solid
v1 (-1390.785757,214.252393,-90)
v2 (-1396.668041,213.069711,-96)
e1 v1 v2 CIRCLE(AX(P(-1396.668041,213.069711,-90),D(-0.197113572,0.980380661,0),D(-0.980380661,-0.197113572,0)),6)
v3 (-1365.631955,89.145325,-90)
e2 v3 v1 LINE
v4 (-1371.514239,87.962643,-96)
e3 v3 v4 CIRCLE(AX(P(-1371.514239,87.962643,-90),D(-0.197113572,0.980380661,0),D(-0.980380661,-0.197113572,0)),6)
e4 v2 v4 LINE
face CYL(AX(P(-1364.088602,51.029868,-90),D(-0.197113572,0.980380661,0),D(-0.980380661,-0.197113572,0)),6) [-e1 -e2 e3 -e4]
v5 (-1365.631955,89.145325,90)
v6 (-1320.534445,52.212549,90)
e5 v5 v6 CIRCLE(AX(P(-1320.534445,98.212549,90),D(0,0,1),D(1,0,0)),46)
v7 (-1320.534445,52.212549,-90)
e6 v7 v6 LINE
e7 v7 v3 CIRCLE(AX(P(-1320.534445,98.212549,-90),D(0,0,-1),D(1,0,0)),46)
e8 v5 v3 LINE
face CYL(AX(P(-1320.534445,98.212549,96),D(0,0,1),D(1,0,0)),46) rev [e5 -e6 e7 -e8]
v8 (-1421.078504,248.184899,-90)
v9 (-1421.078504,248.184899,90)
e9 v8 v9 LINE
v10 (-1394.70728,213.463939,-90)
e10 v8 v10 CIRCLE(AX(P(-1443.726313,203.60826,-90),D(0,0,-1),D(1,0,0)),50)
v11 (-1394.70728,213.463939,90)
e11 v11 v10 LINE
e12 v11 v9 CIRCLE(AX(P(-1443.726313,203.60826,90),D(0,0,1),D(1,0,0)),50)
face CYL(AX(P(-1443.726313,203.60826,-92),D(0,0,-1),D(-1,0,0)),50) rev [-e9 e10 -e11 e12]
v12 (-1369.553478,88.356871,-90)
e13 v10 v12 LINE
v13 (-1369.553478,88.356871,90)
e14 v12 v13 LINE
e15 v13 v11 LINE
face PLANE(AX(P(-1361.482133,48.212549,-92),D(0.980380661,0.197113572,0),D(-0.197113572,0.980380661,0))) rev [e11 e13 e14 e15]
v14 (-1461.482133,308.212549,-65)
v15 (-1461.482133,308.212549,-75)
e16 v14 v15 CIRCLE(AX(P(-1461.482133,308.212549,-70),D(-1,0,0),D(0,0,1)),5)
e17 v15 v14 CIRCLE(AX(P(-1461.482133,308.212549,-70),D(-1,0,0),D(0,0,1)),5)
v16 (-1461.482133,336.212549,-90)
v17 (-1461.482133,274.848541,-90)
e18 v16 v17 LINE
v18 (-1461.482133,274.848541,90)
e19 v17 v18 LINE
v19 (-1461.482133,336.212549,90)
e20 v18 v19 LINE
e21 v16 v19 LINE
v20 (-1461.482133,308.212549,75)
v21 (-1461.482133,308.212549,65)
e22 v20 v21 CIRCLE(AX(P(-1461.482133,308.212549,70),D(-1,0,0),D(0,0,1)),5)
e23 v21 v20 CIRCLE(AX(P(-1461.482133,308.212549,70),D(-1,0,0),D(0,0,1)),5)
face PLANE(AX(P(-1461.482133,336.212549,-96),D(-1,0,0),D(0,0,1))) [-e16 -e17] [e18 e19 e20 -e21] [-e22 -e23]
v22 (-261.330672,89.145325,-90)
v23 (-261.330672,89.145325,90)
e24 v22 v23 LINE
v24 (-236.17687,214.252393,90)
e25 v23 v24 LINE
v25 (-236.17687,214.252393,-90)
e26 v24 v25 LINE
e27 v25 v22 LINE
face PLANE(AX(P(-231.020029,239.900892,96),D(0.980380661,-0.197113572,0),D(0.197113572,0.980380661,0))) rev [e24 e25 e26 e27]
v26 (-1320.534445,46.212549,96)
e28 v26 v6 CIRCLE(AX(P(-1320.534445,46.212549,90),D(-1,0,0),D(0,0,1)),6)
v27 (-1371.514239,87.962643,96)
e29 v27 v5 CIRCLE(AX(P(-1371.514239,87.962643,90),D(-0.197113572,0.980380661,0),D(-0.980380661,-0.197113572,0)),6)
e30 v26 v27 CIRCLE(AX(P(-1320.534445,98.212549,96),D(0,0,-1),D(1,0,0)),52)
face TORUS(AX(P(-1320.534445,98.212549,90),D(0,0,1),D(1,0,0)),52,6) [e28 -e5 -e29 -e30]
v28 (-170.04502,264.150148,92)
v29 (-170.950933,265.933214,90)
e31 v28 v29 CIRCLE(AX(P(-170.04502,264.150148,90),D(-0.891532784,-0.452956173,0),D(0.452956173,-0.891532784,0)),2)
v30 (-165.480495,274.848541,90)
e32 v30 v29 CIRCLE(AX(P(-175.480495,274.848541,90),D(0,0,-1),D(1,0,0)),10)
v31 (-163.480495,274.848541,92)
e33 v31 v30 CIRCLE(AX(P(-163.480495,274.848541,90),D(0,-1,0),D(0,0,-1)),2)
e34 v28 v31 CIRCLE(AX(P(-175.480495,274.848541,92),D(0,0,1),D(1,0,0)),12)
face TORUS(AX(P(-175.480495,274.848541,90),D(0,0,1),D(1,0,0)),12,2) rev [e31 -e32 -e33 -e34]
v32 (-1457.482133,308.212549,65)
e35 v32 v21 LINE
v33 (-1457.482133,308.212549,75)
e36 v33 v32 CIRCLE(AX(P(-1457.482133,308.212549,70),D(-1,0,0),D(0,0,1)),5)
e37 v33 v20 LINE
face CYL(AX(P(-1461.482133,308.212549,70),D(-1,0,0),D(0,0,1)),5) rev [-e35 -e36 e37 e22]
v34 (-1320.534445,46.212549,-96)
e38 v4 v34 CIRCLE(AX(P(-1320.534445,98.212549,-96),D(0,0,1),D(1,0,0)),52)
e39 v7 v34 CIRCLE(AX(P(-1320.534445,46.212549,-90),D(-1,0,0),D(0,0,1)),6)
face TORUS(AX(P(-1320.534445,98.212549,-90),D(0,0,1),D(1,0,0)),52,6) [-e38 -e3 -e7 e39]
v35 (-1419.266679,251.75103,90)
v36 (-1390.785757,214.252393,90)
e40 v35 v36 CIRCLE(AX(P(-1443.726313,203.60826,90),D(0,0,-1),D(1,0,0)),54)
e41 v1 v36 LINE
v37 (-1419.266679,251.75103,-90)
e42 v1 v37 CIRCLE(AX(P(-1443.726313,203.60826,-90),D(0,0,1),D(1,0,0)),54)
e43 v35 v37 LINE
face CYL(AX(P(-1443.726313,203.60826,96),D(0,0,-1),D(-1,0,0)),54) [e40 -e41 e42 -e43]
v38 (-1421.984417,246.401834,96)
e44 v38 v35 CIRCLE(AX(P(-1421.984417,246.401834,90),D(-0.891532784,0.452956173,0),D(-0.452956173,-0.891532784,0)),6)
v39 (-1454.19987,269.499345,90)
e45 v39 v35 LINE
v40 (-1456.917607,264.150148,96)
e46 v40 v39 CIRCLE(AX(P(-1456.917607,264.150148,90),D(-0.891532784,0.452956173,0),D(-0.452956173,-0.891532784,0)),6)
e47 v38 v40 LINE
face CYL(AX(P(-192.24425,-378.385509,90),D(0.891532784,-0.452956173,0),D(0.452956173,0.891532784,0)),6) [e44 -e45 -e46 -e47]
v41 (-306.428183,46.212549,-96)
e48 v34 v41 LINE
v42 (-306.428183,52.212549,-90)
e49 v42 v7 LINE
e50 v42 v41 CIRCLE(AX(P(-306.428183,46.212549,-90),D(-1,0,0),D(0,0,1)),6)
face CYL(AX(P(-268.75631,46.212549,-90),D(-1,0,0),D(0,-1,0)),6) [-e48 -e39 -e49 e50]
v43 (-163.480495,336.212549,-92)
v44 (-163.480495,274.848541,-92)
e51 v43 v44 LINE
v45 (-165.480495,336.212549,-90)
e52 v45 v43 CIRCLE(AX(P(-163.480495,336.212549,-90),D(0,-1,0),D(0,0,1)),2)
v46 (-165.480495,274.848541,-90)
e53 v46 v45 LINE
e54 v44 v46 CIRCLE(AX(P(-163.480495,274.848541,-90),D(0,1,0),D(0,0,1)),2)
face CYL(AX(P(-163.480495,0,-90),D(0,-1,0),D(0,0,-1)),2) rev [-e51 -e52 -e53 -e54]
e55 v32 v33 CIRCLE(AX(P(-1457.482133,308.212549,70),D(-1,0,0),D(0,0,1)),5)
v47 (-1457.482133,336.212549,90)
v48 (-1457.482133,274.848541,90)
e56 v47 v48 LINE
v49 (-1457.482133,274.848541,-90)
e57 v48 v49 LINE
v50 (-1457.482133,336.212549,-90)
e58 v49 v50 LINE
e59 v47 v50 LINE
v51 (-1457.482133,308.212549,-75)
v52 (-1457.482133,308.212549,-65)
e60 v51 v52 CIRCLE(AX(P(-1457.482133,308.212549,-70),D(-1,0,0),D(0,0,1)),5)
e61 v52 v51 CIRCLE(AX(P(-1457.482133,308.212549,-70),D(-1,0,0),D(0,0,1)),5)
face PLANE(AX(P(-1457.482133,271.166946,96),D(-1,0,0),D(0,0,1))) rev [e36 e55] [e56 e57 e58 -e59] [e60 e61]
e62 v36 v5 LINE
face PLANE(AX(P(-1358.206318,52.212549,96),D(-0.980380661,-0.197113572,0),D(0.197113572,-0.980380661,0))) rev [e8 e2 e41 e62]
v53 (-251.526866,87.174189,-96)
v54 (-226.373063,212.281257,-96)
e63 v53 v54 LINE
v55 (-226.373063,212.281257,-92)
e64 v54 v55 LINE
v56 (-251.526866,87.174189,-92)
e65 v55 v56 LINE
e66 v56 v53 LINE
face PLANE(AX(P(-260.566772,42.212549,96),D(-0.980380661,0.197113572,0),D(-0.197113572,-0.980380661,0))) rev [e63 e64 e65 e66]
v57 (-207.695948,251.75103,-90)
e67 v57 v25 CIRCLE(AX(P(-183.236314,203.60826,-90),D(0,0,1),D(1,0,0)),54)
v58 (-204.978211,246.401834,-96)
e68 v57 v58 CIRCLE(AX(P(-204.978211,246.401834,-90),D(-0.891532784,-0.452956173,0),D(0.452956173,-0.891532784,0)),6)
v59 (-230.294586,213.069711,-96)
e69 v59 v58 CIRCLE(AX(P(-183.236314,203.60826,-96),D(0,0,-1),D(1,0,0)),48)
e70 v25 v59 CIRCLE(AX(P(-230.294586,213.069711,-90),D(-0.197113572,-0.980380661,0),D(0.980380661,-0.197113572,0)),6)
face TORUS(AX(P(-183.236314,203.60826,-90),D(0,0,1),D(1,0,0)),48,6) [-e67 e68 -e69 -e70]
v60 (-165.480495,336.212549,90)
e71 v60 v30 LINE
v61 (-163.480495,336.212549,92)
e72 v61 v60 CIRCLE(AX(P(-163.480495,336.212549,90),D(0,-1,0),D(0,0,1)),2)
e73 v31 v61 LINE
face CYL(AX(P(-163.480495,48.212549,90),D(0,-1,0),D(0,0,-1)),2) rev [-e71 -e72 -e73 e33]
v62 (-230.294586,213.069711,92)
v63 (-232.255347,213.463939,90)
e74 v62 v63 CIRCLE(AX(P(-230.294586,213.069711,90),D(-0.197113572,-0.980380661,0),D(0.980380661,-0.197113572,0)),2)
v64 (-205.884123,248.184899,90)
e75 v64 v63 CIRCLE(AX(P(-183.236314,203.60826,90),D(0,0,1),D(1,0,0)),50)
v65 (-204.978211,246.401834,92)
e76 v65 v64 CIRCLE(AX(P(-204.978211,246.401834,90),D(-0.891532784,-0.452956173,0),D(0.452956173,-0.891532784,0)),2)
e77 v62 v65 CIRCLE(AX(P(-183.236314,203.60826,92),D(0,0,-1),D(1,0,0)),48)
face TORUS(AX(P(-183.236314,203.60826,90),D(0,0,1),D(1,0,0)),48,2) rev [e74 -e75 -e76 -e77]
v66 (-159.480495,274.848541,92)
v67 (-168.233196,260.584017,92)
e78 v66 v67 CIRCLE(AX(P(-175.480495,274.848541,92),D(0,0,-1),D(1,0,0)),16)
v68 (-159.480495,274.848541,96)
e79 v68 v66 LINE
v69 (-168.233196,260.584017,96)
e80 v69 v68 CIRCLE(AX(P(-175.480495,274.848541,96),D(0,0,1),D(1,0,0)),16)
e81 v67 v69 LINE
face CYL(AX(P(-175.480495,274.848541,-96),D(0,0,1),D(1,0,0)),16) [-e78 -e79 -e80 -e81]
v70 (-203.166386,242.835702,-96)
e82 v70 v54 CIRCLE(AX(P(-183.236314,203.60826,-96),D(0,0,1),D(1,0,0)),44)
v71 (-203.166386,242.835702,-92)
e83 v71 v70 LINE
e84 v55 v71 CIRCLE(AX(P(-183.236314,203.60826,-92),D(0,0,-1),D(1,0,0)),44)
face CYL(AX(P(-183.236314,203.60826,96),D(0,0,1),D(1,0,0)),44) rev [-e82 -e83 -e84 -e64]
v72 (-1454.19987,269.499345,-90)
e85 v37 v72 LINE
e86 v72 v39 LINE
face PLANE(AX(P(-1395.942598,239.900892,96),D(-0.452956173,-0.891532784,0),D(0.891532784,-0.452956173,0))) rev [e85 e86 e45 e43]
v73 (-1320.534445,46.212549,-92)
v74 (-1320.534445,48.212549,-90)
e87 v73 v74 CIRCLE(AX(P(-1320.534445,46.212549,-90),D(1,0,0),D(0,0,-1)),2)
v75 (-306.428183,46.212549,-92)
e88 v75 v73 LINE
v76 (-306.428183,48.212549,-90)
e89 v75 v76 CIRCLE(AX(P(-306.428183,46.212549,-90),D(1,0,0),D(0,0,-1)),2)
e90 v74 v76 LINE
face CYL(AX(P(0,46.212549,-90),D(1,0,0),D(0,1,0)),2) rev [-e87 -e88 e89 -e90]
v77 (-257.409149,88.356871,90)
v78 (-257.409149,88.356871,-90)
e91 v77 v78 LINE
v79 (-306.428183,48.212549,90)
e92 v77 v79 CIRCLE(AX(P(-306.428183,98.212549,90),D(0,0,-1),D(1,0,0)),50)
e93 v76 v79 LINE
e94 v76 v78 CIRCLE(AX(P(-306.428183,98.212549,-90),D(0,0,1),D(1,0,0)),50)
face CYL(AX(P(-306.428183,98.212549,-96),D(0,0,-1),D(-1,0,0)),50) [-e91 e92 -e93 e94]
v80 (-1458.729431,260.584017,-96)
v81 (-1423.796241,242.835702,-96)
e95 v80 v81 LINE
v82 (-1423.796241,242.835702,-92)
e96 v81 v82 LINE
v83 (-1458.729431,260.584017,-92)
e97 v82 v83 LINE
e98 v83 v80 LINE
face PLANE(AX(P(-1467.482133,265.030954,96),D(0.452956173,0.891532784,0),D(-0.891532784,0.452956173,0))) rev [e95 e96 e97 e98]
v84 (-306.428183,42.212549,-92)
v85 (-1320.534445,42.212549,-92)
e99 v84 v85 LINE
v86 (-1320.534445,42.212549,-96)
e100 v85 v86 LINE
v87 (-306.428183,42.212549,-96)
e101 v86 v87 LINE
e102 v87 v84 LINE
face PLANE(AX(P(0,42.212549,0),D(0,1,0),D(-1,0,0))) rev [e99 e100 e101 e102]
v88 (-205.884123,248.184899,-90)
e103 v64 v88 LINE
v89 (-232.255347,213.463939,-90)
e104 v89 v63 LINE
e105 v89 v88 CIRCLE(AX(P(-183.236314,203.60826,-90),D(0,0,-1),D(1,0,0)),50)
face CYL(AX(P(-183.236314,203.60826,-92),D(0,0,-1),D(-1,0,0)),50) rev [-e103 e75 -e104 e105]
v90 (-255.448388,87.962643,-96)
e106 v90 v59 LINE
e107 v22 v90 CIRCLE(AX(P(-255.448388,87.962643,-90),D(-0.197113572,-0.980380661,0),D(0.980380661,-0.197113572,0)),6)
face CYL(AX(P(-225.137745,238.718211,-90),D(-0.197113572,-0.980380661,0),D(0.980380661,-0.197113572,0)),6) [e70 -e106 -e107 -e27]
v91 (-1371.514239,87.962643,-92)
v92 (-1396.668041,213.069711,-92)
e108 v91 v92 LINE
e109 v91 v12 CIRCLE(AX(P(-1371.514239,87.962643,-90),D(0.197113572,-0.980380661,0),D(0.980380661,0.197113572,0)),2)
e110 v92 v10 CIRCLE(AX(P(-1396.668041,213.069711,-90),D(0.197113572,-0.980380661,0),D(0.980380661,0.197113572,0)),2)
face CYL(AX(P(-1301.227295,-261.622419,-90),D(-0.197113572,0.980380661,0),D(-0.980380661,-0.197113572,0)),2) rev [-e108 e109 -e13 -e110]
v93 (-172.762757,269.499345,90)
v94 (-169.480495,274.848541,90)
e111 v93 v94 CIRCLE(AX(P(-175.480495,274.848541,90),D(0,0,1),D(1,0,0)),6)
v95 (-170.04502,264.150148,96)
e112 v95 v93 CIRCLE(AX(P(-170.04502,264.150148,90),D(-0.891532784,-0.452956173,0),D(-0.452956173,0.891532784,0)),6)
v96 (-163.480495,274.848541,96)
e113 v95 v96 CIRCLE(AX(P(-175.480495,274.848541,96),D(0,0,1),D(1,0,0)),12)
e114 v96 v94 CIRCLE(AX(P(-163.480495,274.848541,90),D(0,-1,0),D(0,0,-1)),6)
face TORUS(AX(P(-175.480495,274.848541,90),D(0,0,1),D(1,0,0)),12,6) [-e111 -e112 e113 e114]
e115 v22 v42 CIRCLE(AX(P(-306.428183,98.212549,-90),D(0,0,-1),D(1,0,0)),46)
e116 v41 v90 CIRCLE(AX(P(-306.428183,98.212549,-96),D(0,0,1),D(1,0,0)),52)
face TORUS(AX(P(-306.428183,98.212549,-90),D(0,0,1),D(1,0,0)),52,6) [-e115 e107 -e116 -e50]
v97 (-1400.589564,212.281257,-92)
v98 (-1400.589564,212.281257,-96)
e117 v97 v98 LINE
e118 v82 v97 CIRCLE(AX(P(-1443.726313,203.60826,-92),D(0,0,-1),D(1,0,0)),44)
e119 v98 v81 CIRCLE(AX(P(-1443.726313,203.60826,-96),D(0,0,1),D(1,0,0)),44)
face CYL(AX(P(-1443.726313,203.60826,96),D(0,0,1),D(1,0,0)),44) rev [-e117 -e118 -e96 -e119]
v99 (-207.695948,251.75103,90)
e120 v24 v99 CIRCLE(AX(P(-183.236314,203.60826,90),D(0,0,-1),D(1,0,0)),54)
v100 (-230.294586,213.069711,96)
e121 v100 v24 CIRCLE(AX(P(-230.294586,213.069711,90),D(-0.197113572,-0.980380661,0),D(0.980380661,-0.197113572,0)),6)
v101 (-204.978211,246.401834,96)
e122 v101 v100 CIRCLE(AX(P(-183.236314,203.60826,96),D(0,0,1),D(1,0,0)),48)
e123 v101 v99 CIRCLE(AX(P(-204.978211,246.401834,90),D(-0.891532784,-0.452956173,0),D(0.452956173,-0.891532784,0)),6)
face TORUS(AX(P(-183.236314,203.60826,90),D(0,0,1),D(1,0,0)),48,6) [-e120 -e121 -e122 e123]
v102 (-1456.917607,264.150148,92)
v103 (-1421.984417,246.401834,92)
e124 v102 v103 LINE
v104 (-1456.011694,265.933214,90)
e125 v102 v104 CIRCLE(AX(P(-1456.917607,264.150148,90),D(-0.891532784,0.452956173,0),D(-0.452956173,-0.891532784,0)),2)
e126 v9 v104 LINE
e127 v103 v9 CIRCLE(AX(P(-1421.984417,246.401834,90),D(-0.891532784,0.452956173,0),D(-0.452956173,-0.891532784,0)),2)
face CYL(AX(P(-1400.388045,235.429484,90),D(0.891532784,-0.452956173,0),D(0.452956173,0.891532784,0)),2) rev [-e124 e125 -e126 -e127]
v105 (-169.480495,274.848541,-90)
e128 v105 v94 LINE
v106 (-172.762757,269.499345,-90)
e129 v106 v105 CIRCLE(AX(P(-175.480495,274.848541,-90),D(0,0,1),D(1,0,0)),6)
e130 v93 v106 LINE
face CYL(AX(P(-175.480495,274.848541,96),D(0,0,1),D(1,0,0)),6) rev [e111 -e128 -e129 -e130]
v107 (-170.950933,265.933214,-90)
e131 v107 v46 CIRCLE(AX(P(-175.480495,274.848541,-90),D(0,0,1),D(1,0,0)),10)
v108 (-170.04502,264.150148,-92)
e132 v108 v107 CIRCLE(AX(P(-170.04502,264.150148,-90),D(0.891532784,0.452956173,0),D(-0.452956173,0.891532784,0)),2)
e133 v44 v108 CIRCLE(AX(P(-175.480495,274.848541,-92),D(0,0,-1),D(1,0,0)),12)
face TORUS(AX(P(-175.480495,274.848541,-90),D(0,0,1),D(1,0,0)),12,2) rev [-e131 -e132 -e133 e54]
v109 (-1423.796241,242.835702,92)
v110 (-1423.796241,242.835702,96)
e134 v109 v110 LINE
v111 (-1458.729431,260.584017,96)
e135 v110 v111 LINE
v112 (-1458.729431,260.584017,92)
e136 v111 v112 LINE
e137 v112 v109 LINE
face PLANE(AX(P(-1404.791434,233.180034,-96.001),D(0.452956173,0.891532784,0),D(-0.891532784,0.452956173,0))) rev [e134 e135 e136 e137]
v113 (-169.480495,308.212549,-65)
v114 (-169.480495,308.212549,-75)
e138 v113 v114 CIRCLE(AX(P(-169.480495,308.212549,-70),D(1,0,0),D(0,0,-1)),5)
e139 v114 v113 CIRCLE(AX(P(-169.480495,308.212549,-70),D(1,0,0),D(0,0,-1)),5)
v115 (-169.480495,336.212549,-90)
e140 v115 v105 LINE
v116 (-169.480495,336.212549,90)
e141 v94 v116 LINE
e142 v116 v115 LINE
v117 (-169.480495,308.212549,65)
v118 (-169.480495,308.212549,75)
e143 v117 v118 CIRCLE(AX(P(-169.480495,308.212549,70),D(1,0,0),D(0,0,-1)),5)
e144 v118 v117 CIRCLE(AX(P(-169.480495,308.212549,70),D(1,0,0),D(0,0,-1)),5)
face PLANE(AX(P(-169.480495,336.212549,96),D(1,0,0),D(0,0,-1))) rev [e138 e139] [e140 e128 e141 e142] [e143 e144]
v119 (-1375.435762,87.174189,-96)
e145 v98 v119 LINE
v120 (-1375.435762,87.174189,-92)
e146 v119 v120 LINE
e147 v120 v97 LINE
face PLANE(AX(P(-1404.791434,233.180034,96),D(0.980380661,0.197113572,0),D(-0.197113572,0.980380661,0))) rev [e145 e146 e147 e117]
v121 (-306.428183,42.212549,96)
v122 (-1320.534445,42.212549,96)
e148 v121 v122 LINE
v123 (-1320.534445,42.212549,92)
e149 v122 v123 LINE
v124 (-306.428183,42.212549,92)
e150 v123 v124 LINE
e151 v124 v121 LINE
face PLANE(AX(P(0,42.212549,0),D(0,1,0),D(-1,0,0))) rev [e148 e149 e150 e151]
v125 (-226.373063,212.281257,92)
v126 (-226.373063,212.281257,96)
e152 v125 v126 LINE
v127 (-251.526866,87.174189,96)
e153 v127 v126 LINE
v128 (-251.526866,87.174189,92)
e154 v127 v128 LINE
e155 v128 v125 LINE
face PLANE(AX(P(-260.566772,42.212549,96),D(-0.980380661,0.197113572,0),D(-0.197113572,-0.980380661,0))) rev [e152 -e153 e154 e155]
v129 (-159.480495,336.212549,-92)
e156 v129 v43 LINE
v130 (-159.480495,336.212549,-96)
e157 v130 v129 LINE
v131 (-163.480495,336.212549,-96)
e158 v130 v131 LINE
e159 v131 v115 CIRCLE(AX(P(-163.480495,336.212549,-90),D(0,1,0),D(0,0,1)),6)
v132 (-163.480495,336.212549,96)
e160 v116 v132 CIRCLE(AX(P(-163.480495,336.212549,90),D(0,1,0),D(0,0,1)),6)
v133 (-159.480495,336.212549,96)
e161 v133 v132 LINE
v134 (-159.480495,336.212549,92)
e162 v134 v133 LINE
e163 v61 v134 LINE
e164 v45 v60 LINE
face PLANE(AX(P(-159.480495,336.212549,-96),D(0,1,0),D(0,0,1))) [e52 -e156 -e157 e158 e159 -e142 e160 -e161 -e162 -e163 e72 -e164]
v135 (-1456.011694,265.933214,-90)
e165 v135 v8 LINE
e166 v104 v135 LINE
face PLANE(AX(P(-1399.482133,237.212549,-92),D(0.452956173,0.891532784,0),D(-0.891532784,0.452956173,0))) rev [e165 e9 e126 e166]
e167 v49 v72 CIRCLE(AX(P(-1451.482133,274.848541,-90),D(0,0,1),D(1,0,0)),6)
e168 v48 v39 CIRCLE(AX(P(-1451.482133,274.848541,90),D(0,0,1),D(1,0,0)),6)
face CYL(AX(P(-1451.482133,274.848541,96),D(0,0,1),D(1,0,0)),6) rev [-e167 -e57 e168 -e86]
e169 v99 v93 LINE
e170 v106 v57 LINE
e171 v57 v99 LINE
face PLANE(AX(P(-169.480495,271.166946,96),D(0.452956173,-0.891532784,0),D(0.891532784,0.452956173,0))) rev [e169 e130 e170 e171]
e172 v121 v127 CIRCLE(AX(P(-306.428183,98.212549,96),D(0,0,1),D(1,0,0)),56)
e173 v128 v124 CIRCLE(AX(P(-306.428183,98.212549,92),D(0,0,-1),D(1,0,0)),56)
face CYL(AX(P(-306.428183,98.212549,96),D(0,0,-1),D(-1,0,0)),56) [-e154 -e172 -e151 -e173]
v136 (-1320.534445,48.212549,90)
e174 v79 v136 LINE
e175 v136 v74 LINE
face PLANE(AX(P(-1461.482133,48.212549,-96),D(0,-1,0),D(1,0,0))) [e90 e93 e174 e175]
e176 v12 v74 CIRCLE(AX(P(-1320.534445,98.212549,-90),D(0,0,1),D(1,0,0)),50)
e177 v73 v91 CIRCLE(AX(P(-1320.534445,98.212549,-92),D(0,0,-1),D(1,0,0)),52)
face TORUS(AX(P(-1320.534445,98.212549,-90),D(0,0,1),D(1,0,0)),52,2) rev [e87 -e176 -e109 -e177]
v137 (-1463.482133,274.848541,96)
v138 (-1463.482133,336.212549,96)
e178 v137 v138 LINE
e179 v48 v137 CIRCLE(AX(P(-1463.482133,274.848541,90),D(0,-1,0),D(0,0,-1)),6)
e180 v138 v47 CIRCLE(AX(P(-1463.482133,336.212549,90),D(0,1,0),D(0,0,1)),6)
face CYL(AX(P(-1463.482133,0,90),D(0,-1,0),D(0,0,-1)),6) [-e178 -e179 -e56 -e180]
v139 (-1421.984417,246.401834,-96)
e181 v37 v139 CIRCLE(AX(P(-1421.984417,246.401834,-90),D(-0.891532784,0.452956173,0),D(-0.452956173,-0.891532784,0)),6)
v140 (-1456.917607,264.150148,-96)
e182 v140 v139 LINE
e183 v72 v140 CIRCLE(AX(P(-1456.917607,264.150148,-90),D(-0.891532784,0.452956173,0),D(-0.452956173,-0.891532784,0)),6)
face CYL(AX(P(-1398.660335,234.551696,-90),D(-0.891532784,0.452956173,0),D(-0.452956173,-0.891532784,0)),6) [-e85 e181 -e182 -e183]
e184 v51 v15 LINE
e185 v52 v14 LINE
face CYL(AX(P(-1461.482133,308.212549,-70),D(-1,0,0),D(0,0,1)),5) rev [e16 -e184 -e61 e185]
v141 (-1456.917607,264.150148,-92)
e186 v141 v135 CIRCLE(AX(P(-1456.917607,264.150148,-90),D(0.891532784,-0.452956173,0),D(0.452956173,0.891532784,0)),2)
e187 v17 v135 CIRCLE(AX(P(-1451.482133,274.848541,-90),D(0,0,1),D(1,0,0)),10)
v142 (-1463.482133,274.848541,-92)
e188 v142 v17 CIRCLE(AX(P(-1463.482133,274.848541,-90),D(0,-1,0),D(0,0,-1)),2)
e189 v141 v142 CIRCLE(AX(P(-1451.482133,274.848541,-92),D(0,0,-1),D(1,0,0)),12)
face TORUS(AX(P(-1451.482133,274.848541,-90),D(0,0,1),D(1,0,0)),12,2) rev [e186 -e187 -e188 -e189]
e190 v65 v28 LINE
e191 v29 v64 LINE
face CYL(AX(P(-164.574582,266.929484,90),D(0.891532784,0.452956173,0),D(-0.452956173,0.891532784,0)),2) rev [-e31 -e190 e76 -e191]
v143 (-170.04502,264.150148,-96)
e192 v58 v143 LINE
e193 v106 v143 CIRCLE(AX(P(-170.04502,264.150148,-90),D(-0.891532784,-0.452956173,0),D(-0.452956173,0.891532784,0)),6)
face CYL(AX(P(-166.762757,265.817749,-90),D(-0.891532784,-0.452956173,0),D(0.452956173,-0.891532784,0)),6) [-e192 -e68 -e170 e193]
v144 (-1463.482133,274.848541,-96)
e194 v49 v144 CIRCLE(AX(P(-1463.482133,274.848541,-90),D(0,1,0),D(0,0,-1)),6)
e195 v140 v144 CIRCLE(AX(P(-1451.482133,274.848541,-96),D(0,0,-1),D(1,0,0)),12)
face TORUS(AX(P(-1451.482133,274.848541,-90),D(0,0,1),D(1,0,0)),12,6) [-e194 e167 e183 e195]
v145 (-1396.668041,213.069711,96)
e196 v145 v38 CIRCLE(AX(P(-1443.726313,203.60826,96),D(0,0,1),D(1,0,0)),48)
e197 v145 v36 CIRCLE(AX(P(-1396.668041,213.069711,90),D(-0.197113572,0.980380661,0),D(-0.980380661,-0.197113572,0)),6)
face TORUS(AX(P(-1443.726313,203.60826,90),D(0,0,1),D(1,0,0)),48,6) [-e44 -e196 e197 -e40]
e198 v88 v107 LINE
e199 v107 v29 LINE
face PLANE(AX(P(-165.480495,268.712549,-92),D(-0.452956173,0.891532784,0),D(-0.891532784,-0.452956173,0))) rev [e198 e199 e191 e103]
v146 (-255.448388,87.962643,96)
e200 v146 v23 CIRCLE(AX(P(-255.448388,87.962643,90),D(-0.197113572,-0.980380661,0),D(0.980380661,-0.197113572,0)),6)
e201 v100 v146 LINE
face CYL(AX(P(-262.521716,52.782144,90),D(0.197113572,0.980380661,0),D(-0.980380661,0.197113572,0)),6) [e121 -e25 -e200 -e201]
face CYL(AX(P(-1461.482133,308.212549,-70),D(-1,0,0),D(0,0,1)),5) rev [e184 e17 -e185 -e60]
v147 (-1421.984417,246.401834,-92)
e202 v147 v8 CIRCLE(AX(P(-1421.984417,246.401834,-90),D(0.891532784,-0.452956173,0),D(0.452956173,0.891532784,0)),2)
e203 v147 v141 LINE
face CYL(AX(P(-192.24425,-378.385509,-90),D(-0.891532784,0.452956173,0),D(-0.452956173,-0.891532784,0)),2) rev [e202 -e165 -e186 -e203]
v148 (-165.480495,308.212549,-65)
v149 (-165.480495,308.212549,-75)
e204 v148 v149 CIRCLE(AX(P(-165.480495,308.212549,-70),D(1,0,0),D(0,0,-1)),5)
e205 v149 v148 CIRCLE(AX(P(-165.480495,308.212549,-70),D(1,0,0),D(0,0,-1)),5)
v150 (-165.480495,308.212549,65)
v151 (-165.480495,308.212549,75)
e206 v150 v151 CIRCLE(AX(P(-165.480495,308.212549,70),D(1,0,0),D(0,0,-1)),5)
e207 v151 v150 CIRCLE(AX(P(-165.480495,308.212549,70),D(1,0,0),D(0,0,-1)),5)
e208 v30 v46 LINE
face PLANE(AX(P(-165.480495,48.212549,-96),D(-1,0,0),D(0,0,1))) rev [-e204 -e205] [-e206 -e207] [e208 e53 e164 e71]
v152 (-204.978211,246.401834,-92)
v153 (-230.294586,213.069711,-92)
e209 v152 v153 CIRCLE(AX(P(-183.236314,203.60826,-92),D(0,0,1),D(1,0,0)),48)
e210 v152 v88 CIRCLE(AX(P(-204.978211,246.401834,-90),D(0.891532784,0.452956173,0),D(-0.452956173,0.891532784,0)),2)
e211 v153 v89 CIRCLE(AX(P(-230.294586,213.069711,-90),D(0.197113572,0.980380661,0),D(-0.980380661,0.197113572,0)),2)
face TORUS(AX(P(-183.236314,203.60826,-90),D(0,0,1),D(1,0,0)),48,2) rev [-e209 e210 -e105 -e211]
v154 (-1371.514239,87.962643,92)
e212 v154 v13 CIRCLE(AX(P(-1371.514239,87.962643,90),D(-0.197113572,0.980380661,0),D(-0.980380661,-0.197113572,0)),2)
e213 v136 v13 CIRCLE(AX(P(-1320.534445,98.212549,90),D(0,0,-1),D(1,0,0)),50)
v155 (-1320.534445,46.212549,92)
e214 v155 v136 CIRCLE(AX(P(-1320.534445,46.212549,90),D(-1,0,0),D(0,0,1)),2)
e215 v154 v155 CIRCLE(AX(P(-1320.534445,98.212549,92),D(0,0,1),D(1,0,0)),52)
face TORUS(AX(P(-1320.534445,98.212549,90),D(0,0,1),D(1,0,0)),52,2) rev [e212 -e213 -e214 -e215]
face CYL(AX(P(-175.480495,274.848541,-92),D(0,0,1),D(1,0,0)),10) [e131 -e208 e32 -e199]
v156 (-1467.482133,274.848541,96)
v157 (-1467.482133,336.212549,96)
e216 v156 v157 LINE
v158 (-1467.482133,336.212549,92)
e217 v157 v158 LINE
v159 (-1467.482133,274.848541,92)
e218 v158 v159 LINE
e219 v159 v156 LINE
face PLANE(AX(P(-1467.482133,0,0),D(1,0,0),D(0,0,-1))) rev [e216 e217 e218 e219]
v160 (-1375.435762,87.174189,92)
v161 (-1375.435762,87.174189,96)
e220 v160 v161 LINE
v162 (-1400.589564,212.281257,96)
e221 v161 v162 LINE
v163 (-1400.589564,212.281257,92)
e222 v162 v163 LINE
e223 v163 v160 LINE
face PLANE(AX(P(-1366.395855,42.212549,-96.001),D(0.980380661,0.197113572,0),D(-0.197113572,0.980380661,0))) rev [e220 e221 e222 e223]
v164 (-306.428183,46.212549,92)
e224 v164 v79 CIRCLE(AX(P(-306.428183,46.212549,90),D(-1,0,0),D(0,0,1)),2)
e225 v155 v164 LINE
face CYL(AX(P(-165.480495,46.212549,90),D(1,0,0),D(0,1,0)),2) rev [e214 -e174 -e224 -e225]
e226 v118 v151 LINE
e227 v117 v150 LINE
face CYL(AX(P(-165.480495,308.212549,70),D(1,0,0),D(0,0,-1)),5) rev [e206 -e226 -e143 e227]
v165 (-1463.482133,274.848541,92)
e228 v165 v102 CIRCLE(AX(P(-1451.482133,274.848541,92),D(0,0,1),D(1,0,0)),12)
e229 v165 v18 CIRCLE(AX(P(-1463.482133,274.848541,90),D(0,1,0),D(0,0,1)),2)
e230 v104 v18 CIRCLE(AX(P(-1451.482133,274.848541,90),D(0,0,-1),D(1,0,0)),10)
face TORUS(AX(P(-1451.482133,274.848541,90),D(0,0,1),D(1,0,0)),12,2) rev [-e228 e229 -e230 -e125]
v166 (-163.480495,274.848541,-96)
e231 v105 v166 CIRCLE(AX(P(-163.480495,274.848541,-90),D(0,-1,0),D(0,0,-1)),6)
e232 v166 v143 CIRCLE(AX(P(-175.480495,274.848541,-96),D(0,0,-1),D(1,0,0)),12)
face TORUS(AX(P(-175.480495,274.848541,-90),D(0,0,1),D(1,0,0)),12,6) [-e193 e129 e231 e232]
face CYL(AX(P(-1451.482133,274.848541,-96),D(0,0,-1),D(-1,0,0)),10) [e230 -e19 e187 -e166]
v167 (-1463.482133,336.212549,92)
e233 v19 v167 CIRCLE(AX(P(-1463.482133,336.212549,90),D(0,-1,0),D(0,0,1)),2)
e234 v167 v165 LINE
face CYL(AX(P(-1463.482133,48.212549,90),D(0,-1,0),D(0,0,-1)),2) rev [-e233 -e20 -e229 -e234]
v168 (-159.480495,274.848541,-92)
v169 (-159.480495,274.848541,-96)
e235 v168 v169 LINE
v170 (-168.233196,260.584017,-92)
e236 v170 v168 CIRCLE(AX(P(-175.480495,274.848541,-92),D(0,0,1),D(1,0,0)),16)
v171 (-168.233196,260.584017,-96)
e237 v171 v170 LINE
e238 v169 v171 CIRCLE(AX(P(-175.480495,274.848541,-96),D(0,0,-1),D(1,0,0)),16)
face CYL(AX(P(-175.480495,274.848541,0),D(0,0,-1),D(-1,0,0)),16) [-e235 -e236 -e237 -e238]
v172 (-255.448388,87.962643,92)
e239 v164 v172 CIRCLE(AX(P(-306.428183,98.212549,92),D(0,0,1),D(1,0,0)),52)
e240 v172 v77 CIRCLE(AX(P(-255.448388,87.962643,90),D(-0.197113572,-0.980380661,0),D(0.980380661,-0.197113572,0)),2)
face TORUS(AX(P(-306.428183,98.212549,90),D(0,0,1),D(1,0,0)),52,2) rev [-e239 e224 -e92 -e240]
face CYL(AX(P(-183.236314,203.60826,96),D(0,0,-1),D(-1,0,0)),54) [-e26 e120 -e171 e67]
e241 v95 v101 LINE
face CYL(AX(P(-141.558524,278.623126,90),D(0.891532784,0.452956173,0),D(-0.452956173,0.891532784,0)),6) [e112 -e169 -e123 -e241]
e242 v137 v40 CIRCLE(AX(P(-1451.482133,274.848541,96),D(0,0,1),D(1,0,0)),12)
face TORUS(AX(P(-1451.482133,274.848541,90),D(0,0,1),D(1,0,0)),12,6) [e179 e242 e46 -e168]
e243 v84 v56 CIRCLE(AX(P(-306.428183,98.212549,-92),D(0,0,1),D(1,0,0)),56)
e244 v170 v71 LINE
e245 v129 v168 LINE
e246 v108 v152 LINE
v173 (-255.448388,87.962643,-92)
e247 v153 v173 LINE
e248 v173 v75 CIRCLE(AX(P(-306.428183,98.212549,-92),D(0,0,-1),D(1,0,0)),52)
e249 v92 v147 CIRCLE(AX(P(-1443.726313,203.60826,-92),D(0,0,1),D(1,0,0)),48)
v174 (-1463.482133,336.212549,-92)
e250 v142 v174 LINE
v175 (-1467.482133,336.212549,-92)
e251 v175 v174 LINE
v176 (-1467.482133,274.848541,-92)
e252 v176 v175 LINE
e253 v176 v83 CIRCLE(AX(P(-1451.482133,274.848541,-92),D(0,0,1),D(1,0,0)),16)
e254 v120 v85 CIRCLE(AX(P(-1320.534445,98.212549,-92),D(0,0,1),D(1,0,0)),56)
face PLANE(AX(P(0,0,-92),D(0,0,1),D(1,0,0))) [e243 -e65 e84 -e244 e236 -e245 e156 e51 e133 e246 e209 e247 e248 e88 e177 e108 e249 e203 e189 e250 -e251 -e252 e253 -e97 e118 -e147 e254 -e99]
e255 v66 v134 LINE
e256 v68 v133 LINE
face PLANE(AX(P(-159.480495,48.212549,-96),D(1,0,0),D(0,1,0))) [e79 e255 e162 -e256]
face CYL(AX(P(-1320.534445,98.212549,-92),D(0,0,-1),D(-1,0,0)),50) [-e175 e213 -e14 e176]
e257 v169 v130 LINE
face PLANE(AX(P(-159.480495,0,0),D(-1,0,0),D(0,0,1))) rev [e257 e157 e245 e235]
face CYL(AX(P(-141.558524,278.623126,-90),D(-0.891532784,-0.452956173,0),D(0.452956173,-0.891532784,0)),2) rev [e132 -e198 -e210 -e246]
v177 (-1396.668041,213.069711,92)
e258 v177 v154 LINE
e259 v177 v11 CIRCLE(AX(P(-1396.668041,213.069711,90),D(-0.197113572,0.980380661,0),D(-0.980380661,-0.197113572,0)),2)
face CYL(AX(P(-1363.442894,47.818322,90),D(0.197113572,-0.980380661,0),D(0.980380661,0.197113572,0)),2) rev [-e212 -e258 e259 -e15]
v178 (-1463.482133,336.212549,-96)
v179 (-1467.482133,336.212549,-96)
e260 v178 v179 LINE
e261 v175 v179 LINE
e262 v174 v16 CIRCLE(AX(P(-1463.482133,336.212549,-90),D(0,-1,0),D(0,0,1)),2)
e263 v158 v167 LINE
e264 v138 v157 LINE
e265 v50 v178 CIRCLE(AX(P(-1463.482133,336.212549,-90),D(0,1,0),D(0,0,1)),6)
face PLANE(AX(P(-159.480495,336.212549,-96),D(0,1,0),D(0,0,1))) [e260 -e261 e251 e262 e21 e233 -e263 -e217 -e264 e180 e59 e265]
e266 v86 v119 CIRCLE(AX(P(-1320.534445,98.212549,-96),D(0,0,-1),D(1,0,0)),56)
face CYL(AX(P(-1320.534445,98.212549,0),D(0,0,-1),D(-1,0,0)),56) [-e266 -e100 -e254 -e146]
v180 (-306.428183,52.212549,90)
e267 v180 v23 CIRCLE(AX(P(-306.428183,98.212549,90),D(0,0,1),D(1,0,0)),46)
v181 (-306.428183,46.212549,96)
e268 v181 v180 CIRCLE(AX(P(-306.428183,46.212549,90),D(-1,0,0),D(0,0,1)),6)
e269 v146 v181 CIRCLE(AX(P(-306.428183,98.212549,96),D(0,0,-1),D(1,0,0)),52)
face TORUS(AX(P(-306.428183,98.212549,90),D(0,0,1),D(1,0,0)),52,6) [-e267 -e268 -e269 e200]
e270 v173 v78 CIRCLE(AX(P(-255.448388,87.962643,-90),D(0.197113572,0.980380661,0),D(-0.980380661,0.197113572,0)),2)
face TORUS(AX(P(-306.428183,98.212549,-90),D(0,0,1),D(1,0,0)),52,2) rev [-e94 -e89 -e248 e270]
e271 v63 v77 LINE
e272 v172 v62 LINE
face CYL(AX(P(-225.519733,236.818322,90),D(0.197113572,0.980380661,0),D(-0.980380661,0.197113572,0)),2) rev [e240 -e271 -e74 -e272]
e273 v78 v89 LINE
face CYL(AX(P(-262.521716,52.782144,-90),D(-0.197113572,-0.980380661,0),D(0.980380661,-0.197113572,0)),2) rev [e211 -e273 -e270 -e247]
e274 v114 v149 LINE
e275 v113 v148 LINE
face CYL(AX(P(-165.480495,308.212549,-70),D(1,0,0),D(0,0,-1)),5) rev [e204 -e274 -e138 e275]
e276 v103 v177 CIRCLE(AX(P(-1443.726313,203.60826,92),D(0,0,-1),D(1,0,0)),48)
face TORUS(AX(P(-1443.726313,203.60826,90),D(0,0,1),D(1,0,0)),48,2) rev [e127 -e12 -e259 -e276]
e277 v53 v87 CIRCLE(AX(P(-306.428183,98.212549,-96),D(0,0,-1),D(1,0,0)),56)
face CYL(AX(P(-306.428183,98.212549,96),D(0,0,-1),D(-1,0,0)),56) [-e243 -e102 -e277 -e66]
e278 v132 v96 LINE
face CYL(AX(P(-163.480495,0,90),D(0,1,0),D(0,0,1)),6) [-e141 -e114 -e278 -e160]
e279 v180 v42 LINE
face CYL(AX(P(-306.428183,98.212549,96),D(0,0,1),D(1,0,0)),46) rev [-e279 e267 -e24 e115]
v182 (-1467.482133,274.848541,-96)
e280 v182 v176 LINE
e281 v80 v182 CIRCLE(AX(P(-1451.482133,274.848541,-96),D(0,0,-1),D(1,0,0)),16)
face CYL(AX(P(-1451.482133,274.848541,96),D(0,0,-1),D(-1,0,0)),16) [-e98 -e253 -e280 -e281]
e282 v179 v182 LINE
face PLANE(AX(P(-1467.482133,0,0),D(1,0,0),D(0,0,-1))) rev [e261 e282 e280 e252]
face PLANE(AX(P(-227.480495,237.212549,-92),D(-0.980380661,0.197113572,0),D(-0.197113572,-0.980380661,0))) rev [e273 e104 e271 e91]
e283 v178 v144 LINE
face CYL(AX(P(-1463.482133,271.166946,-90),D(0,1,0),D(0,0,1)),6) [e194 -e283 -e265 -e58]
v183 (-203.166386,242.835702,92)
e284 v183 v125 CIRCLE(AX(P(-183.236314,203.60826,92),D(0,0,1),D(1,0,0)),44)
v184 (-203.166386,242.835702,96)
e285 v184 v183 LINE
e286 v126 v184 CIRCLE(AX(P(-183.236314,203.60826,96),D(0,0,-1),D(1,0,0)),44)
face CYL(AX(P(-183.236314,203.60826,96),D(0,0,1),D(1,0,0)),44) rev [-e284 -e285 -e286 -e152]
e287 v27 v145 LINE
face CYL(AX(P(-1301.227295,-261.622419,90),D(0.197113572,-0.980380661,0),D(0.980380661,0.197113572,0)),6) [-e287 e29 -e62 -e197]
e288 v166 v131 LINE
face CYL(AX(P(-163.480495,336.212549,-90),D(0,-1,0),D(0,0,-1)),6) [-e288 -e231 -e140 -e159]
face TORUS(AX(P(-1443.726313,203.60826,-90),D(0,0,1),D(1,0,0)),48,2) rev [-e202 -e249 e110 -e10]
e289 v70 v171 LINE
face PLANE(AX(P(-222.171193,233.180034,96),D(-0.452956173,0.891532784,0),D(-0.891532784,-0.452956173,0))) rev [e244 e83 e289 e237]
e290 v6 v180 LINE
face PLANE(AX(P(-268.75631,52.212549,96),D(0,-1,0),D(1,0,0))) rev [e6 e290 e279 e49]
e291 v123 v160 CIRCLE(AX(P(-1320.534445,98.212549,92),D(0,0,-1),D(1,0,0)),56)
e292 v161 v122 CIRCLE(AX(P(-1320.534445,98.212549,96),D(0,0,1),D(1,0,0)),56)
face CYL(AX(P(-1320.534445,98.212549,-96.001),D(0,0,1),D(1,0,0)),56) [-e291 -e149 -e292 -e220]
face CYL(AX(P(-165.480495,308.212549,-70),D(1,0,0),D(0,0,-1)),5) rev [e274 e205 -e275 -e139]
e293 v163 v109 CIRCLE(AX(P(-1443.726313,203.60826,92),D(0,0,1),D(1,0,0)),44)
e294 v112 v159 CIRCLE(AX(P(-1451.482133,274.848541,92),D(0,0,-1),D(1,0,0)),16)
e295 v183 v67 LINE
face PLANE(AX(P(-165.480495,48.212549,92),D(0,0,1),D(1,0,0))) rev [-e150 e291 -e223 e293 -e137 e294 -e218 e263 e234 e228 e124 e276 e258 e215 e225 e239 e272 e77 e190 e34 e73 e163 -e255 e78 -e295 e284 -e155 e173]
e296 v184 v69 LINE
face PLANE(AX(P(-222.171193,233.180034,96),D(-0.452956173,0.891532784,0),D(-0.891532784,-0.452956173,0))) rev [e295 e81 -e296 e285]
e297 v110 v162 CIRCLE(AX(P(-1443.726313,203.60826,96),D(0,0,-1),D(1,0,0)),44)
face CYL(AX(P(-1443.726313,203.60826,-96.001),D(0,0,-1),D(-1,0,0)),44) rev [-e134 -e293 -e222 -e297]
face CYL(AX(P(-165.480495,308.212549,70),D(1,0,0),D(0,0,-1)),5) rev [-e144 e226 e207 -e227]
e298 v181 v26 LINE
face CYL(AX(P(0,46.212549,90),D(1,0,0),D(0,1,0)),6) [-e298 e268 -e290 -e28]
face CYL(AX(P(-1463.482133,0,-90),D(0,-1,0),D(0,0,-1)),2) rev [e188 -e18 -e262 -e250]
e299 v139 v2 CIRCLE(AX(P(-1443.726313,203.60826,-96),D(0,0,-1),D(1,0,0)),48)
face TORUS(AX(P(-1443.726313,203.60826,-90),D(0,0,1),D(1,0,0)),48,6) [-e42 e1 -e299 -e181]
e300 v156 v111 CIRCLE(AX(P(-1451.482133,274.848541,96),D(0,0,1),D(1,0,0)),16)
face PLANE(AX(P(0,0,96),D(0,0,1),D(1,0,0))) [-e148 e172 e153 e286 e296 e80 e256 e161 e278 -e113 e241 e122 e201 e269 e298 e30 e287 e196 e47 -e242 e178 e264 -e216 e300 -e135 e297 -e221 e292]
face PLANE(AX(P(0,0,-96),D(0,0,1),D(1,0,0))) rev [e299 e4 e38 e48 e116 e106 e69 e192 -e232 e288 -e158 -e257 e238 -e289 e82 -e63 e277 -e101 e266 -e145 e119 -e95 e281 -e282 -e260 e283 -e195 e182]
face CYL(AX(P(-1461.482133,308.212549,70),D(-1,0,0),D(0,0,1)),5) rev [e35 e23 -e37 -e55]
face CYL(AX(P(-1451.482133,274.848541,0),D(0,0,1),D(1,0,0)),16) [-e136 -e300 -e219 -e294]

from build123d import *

# Parameters (mm, degrees)
SKETCH1_W                      = 1302.001638203
SKETCH1_H                      = 288
BOSS_EXTRUDE1_DEPTH            = 192
SKETCH2_W                      = 6
SKETCH2_H                      = 188
CUT_EXTRUDE1_DEPTH             = 1493.678808133
CUT_EXTRUDE2_DEPTH             = 184
SKETCH4_W                      = 1302.001638203
SKETCH4_H                      = 4
BOSS_EXTRUDE2_DEPTH            = 6
CUT_EXTRUDE3_DEPTH             = 184
SKETCH6_W                      = 4
SKETCH6_H                      = 294
BOSS_EXTRUDE3_DEPTH            = 6
SKETCH7_W                      = 4
SKETCH7_H                      = 288
BOSS_EXTRUDE4_DEPTH            = 6
SKETCH8_W                      = 1302.001638203
SKETCH8_H                      = 4
BOSS_EXTRUDE5_DEPTH            = 6
SKETCH9_W                      = 4
SKETCH9_H                      = 294
BOSS_EXTRUDE6_DEPTH            = 6
CUT_EXTRUDE4_DEPTH             = 1518.19698392
CUT_EXTRUDE5_REACH             = 1519.698
CUT_EXTRUDE6_DEPTH             = 1518.697825002
CUT_EXTRUDE7_DEPTH             = 1518.697825002
CUT_EXTRUDE8_DEPTH             = 1518.697825002
F_10_0_10_DIAMETER_HOLE1_D     = 10
F_10_0_10_DIAMETER_HOLE1_DEPTH = 4
F_10_0_10_DIAMETER_HOLE2_D     = 10
F_10_0_10_DIAMETER_HOLE2_DEPTH = 1302.001638202
FILLET1_R                      = 44
FILLET2_R                      = 10
FILLET3_R                      = 45.999999999
FILLET4_R                      = 50
FILLET5_R                      = 54
FILLET6_R                      = 2
FILLET7_R                      = 6
FILLET8_R                      = 16
FILLET9_R                      = 55.999999999


with BuildPart() as part:
    # Sketch1 → Boss-Extrude1 (new body)
    with BuildSketch(Plane.XY.offset(96)):
        with Locations((-810.481313615, 192.212549099)):
            Rectangle(SKETCH1_W, SKETCH1_H)
    extrude(amount=-BOSS_EXTRUDE1_DEPTH)

    # Sketch2 → Cut-Extrude1 (cut, through all)
    with BuildSketch(Plane(origin=(0, 336.212549099, 0), x_dir=(-1, 0, 0), z_dir=(0, 1, 0))):
        with Locations((162.480494514, -2)):
            Rectangle(SKETCH2_W, SKETCH2_H)
    extrude(amount=-CUT_EXTRUDE1_DEPTH, mode=Mode.SUBTRACT)

    # Sketch3 → Cut-Extrude2 (cut)
    with BuildSketch(Plane.XY.offset(92)):
        Polygon((-165.480494514, 48.212549099), (-165.480494514, 268.712549099), (-227.480494514, 237.212549099), (-265.480494514, 48.212549099), align=None)
    extrude(amount=-CUT_EXTRUDE2_DEPTH, mode=Mode.SUBTRACT)

    # Sketch4 → Boss-Extrude2 (add)
    with BuildSketch(Plane.XZ.offset(-48.212549099)):
        with Locations((-810.481313615, 94)):
            Rectangle(SKETCH4_W, SKETCH4_H)
    extrude(amount=BOSS_EXTRUDE2_DEPTH)

    # Sketch5 → Cut-Extrude3 (cut)
    with BuildSketch(Plane.XY.offset(92)):
        Polygon((-1461.482132717, 268.712549099), (-1461.482132717, 48.212549099), (-1361.482132717, 48.212549099), (-1399.482132717, 237.212549099), align=None)
    extrude(amount=-CUT_EXTRUDE3_DEPTH, mode=Mode.SUBTRACT)

    # Sketch6 → Boss-Extrude3 (add)
    with BuildSketch(Plane.ZY.offset(1461.482132717)):
        with Locations((94, 189.212549099)):
            Rectangle(SKETCH6_W, SKETCH6_H)
    extrude(amount=BOSS_EXTRUDE3_DEPTH)

    # Sketch7 → Boss-Extrude4 (add)
    with BuildSketch(Plane(origin=(-165.480494514, 0, 0), x_dir=(0, 0, -1), z_dir=(1, 0, 0))):
        with Locations((94, 192.212549099)):
            Rectangle(SKETCH7_W, SKETCH7_H)
    extrude(amount=BOSS_EXTRUDE4_DEPTH)

    # Sketch8 → Boss-Extrude5 (add)
    with BuildSketch(Plane.XZ.offset(-48.212549099)):
        with Locations((-810.481313615, -94)):
            Rectangle(SKETCH8_W, SKETCH8_H)
    extrude(amount=BOSS_EXTRUDE5_DEPTH)

    # Sketch9 → Boss-Extrude6 (add)
    with BuildSketch(Plane.ZY.offset(1461.482132717)):
        with Locations((-94, 189.212549099)):
            Rectangle(SKETCH9_W, SKETCH9_H)
    extrude(amount=BOSS_EXTRUDE6_DEPTH)

    # Sketch10 → Cut-Extrude4 (cut, through all)
    with BuildSketch(Plane(origin=(0, 0, 92), x_dir=(-1, 0, 0), z_dir=(0, 0, -1))):
        Polygon((222.171192902, 233.180034395), (159.480494514, 265.030953737), (159.480494514, 42.212549099), (260.566771956, 42.212549099), align=None)
    extrude(amount=-CUT_EXTRUDE4_DEPTH, mode=Mode.SUBTRACT)

    # Sketch11 → Cut-Extrude5 (cut, up to next)
    with BuildSketch(Plane.XY.offset(96), mode=Mode.PRIVATE) as cut_extrude5_sk1:
        Polygon((-1404.79143433, 233.180034395), (-1467.482132717, 265.030953737), (-1467.482132717, 42.212549099), (-1366.395855275, 42.212549099), align=None)
    cut_extrude5_tool1 = extrude(cut_extrude5_sk1.sketch, amount=-CUT_EXTRUDE5_REACH, mode=Mode.PRIVATE) & part.part
    add(cut_extrude5_tool1.solids().sort_by_distance((-1427.035862, 137.049675, 96))[0], mode=Mode.SUBTRACT)

    # Sketch12 → Cut-Extrude6 (cut, through all)
    with BuildSketch(Plane(origin=(0, 0, -96), x_dir=(-1, 0, 0), z_dir=(0, 0, -1))):
        Polygon((1457.482132717, 336.212549099), (169.480494514, 336.212549099), (169.480494514, 271.166946007), (231.020028923, 239.900892235), (268.756309553, 52.212549099), (1358.206317678, 52.212549099), (1395.942598308, 239.900892235), (1457.482132717, 271.166946007), align=None)
    extrude(amount=-CUT_EXTRUDE6_DEPTH, mode=Mode.SUBTRACT)

    # Sketch13 → Cut-Extrude7 (cut, through all)
    with BuildSketch(Plane(origin=(0, 0, -96), x_dir=(-1, 0, 0), z_dir=(0, 0, -1))):
        Polygon((1467.482132717, 265.030953737), (1404.79143433, 233.180034395), (1366.395855275, 42.212549099), (1467.482132717, 42.212549099), align=None)
    extrude(amount=-CUT_EXTRUDE7_DEPTH, mode=Mode.SUBTRACT)

    # Sketch14 → Cut-Extrude8 (cut, through all)
    with BuildSketch(Plane(origin=(0, 0, -96), x_dir=(-1, 0, 0), z_dir=(0, 0, -1))):
        Polygon((222.171192902, 233.180034395), (159.480494514, 265.030953737), (159.480494514, 42.212549099), (260.566771956, 42.212549099), align=None)
    extrude(amount=-CUT_EXTRUDE8_DEPTH, mode=Mode.SUBTRACT)

    # Ø10.0 (10) Diameter Hole1
    with Locations(Plane.ZY.offset(1461.482132717)):
        with Locations((-70, 308.212549099), (70, 308.212549099)):
            Hole(F_10_0_10_DIAMETER_HOLE1_D / 2, depth=F_10_0_10_DIAMETER_HOLE1_DEPTH)

    # Ø10.0 (10) Diameter Hole2
    with Locations(Plane(origin=(-165.480494514, 0, 0), x_dir=(0, 0, -1), z_dir=(1, 0, 0))):
        with Locations((70, 308.212549099), (-70, 308.212549099)):
            Hole(F_10_0_10_DIAMETER_HOLE2_D / 2, depth=F_10_0_10_DIAMETER_HOLE2_DEPTH)

    # Fillet1
    fillet1_edges = [part.edges().sort_by_distance(p)[0] for p in [
        (-222.171192902, 233.180034395, 94),
        (-1404.79143433, 233.180034395, 94),
        (-1404.79143433, 233.180034395, -94),
        (-222.171192902, 233.180034395, -94),
    ]]
    fillet(fillet1_edges, radius=FILLET1_R)

    # Fillet2
    fillet2_edges = [part.edges().sort_by_distance(p)[0] for p in [
        (-165.480494514, 268.712549099, 0),
        (-1461.482132717, 268.712549099, 0),
    ]]
    fillet(fillet2_edges, radius=FILLET2_R)

    # Fillet3
    fillet3_edges = [part.edges().sort_by_distance(p)[0] for p in [
        (-1358.206317678, 52.212549099, 0),
        (-268.756309553, 52.212549099, 0),
    ]]
    fillet(fillet3_edges, radius=FILLET3_R)

    # Fillet4
    fillet4_edges = [part.edges().sort_by_distance(p)[0] for p in [
        (-265.480494514, 48.212549099, 0),
        (-227.480494514, 237.212549099, 0),
        (-1399.482132717, 237.212549099, 0),
        (-1361.482132717, 48.212549099, 0),
    ]]
    fillet(fillet4_edges, radius=FILLET4_R)

    # Fillet5
    fillet5_edges = [part.edges().sort_by_distance(p)[0] for p in [
        (-1395.942598308, 239.900892235, 0),
        (-231.020028923, 239.900892235, 0),
    ]]
    fillet(fillet5_edges, radius=FILLET5_R)

    # Fillet6
    fillet6_edges = [part.edges().sort_by_distance(p)[0] for p in [
        (-1461.482132717, 305.530545234, -92),
        (-188.417527915, 257.059056323, 92),
        (-188.417527915, 257.059056323, -92),
        (-165.480494514, 305.530545234, 92),
        (-1460.005501102, 269.618609116, 92),
        (-1460.005501102, 269.618609116, -92),
        (-166.957126129, 269.618609116, 92),
        (-166.957126129, 269.618609116, -92),
        (-1438.545099316, 257.059056323, 92),
        (-1438.545099316, 257.059056323, -92),
        (-1382.130378776, 150.910404501, 92),
        (-813.481313616, 48.212549099, 92),
        (-244.832248455, 150.910404501, 92),
        (-223.0536514, 233.850278267, 92),
        (-1403.908975831, 233.850278267, 92),
        (-1382.130378776, 150.910404501, -92),
        (-244.832248455, 150.910404501, -92),
        (-813.481313616, 48.212549099, -92),
        (-223.0536514, 233.850278267, -92),
        (-1403.908975831, 233.850278267, -92),
        (-274.748409223, 59.529323213, 92),
        (-274.748409223, 59.529323213, -92),
        (-1352.214218008, 59.529323213, 92),
        (-1352.214218008, 59.529323213, -92),
        (-1461.482132717, 305.530545234, 92),
        (-165.480494514, 305.530545234, -92),
    ]]
    fillet(fillet6_edges, radius=FILLET6_R)

    # Fillet7
    fillet7_edges = [part.edges().sort_by_distance(p)[0] for p in [
        (-1457.482132717, 303.689747553, 96),
        (-1457.482132717, 271.166946007, 0),
        (-188.588221124, 261.458988133, 96),
        (-169.480494514, 303.689747553, 96),
        (-169.480494514, 271.166946007, 0),
        (-1457.482132717, 303.689747553, -96),
        (-169.480494514, 303.689747553, -96),
        (-188.588221124, 261.458988133, -96),
        (-813.481313616, 52.212549099, -96),
        (-813.481313616, 52.212549099, 96),
        (-1378.208856134, 151.698858788, -96),
        (-1378.208856134, 151.698858788, 96),
        (-277.282791085, 62.623981284, -96),
        (-277.282791085, 62.623981284, 96),
        (-1349.679836146, 62.623981284, -96),
        (-1349.679836146, 62.623981284, 96),
        (-248.753771097, 151.698858788, -96),
        (-248.753771097, 151.698858788, 96),
        (-1438.374406107, 261.458988133, -96),
        (-1400.723588872, 236.269639737, -96),
        (-226.23903836, 236.269639737, -96),
        (-1438.374406107, 261.458988133, 96),
        (-1400.723588872, 236.269639737, 96),
        (-226.23903836, 236.269639737, 96),
    ]]
    fillet(fillet7_edges, radius=FILLET7_R)

    # Fillet8
    fillet8_edges = [part.edges().sort_by_distance(p)[0] for p in [
        (-159.480494514, 265.030953737, 94),
        (-1467.482132717, 265.030953737, 94),
        (-1467.482132717, 265.030953737, -94),
        (-159.480494514, 265.030953737, -94),
    ]]
    fillet(fillet8_edges, radius=FILLET8_R)

    # Fillet9
    fillet9_edges = [part.edges().sort_by_distance(p)[0] for p in [
        (-260.566771956, 42.212549099, 94),
        (-1366.395855275, 42.212549099, 94),
        (-1366.395855275, 42.212549099, -94),
        (-260.566771956, 42.212549099, -94),
    ]]
    fillet(fillet9_edges, radius=FILLET9_R)


solid = part.part
